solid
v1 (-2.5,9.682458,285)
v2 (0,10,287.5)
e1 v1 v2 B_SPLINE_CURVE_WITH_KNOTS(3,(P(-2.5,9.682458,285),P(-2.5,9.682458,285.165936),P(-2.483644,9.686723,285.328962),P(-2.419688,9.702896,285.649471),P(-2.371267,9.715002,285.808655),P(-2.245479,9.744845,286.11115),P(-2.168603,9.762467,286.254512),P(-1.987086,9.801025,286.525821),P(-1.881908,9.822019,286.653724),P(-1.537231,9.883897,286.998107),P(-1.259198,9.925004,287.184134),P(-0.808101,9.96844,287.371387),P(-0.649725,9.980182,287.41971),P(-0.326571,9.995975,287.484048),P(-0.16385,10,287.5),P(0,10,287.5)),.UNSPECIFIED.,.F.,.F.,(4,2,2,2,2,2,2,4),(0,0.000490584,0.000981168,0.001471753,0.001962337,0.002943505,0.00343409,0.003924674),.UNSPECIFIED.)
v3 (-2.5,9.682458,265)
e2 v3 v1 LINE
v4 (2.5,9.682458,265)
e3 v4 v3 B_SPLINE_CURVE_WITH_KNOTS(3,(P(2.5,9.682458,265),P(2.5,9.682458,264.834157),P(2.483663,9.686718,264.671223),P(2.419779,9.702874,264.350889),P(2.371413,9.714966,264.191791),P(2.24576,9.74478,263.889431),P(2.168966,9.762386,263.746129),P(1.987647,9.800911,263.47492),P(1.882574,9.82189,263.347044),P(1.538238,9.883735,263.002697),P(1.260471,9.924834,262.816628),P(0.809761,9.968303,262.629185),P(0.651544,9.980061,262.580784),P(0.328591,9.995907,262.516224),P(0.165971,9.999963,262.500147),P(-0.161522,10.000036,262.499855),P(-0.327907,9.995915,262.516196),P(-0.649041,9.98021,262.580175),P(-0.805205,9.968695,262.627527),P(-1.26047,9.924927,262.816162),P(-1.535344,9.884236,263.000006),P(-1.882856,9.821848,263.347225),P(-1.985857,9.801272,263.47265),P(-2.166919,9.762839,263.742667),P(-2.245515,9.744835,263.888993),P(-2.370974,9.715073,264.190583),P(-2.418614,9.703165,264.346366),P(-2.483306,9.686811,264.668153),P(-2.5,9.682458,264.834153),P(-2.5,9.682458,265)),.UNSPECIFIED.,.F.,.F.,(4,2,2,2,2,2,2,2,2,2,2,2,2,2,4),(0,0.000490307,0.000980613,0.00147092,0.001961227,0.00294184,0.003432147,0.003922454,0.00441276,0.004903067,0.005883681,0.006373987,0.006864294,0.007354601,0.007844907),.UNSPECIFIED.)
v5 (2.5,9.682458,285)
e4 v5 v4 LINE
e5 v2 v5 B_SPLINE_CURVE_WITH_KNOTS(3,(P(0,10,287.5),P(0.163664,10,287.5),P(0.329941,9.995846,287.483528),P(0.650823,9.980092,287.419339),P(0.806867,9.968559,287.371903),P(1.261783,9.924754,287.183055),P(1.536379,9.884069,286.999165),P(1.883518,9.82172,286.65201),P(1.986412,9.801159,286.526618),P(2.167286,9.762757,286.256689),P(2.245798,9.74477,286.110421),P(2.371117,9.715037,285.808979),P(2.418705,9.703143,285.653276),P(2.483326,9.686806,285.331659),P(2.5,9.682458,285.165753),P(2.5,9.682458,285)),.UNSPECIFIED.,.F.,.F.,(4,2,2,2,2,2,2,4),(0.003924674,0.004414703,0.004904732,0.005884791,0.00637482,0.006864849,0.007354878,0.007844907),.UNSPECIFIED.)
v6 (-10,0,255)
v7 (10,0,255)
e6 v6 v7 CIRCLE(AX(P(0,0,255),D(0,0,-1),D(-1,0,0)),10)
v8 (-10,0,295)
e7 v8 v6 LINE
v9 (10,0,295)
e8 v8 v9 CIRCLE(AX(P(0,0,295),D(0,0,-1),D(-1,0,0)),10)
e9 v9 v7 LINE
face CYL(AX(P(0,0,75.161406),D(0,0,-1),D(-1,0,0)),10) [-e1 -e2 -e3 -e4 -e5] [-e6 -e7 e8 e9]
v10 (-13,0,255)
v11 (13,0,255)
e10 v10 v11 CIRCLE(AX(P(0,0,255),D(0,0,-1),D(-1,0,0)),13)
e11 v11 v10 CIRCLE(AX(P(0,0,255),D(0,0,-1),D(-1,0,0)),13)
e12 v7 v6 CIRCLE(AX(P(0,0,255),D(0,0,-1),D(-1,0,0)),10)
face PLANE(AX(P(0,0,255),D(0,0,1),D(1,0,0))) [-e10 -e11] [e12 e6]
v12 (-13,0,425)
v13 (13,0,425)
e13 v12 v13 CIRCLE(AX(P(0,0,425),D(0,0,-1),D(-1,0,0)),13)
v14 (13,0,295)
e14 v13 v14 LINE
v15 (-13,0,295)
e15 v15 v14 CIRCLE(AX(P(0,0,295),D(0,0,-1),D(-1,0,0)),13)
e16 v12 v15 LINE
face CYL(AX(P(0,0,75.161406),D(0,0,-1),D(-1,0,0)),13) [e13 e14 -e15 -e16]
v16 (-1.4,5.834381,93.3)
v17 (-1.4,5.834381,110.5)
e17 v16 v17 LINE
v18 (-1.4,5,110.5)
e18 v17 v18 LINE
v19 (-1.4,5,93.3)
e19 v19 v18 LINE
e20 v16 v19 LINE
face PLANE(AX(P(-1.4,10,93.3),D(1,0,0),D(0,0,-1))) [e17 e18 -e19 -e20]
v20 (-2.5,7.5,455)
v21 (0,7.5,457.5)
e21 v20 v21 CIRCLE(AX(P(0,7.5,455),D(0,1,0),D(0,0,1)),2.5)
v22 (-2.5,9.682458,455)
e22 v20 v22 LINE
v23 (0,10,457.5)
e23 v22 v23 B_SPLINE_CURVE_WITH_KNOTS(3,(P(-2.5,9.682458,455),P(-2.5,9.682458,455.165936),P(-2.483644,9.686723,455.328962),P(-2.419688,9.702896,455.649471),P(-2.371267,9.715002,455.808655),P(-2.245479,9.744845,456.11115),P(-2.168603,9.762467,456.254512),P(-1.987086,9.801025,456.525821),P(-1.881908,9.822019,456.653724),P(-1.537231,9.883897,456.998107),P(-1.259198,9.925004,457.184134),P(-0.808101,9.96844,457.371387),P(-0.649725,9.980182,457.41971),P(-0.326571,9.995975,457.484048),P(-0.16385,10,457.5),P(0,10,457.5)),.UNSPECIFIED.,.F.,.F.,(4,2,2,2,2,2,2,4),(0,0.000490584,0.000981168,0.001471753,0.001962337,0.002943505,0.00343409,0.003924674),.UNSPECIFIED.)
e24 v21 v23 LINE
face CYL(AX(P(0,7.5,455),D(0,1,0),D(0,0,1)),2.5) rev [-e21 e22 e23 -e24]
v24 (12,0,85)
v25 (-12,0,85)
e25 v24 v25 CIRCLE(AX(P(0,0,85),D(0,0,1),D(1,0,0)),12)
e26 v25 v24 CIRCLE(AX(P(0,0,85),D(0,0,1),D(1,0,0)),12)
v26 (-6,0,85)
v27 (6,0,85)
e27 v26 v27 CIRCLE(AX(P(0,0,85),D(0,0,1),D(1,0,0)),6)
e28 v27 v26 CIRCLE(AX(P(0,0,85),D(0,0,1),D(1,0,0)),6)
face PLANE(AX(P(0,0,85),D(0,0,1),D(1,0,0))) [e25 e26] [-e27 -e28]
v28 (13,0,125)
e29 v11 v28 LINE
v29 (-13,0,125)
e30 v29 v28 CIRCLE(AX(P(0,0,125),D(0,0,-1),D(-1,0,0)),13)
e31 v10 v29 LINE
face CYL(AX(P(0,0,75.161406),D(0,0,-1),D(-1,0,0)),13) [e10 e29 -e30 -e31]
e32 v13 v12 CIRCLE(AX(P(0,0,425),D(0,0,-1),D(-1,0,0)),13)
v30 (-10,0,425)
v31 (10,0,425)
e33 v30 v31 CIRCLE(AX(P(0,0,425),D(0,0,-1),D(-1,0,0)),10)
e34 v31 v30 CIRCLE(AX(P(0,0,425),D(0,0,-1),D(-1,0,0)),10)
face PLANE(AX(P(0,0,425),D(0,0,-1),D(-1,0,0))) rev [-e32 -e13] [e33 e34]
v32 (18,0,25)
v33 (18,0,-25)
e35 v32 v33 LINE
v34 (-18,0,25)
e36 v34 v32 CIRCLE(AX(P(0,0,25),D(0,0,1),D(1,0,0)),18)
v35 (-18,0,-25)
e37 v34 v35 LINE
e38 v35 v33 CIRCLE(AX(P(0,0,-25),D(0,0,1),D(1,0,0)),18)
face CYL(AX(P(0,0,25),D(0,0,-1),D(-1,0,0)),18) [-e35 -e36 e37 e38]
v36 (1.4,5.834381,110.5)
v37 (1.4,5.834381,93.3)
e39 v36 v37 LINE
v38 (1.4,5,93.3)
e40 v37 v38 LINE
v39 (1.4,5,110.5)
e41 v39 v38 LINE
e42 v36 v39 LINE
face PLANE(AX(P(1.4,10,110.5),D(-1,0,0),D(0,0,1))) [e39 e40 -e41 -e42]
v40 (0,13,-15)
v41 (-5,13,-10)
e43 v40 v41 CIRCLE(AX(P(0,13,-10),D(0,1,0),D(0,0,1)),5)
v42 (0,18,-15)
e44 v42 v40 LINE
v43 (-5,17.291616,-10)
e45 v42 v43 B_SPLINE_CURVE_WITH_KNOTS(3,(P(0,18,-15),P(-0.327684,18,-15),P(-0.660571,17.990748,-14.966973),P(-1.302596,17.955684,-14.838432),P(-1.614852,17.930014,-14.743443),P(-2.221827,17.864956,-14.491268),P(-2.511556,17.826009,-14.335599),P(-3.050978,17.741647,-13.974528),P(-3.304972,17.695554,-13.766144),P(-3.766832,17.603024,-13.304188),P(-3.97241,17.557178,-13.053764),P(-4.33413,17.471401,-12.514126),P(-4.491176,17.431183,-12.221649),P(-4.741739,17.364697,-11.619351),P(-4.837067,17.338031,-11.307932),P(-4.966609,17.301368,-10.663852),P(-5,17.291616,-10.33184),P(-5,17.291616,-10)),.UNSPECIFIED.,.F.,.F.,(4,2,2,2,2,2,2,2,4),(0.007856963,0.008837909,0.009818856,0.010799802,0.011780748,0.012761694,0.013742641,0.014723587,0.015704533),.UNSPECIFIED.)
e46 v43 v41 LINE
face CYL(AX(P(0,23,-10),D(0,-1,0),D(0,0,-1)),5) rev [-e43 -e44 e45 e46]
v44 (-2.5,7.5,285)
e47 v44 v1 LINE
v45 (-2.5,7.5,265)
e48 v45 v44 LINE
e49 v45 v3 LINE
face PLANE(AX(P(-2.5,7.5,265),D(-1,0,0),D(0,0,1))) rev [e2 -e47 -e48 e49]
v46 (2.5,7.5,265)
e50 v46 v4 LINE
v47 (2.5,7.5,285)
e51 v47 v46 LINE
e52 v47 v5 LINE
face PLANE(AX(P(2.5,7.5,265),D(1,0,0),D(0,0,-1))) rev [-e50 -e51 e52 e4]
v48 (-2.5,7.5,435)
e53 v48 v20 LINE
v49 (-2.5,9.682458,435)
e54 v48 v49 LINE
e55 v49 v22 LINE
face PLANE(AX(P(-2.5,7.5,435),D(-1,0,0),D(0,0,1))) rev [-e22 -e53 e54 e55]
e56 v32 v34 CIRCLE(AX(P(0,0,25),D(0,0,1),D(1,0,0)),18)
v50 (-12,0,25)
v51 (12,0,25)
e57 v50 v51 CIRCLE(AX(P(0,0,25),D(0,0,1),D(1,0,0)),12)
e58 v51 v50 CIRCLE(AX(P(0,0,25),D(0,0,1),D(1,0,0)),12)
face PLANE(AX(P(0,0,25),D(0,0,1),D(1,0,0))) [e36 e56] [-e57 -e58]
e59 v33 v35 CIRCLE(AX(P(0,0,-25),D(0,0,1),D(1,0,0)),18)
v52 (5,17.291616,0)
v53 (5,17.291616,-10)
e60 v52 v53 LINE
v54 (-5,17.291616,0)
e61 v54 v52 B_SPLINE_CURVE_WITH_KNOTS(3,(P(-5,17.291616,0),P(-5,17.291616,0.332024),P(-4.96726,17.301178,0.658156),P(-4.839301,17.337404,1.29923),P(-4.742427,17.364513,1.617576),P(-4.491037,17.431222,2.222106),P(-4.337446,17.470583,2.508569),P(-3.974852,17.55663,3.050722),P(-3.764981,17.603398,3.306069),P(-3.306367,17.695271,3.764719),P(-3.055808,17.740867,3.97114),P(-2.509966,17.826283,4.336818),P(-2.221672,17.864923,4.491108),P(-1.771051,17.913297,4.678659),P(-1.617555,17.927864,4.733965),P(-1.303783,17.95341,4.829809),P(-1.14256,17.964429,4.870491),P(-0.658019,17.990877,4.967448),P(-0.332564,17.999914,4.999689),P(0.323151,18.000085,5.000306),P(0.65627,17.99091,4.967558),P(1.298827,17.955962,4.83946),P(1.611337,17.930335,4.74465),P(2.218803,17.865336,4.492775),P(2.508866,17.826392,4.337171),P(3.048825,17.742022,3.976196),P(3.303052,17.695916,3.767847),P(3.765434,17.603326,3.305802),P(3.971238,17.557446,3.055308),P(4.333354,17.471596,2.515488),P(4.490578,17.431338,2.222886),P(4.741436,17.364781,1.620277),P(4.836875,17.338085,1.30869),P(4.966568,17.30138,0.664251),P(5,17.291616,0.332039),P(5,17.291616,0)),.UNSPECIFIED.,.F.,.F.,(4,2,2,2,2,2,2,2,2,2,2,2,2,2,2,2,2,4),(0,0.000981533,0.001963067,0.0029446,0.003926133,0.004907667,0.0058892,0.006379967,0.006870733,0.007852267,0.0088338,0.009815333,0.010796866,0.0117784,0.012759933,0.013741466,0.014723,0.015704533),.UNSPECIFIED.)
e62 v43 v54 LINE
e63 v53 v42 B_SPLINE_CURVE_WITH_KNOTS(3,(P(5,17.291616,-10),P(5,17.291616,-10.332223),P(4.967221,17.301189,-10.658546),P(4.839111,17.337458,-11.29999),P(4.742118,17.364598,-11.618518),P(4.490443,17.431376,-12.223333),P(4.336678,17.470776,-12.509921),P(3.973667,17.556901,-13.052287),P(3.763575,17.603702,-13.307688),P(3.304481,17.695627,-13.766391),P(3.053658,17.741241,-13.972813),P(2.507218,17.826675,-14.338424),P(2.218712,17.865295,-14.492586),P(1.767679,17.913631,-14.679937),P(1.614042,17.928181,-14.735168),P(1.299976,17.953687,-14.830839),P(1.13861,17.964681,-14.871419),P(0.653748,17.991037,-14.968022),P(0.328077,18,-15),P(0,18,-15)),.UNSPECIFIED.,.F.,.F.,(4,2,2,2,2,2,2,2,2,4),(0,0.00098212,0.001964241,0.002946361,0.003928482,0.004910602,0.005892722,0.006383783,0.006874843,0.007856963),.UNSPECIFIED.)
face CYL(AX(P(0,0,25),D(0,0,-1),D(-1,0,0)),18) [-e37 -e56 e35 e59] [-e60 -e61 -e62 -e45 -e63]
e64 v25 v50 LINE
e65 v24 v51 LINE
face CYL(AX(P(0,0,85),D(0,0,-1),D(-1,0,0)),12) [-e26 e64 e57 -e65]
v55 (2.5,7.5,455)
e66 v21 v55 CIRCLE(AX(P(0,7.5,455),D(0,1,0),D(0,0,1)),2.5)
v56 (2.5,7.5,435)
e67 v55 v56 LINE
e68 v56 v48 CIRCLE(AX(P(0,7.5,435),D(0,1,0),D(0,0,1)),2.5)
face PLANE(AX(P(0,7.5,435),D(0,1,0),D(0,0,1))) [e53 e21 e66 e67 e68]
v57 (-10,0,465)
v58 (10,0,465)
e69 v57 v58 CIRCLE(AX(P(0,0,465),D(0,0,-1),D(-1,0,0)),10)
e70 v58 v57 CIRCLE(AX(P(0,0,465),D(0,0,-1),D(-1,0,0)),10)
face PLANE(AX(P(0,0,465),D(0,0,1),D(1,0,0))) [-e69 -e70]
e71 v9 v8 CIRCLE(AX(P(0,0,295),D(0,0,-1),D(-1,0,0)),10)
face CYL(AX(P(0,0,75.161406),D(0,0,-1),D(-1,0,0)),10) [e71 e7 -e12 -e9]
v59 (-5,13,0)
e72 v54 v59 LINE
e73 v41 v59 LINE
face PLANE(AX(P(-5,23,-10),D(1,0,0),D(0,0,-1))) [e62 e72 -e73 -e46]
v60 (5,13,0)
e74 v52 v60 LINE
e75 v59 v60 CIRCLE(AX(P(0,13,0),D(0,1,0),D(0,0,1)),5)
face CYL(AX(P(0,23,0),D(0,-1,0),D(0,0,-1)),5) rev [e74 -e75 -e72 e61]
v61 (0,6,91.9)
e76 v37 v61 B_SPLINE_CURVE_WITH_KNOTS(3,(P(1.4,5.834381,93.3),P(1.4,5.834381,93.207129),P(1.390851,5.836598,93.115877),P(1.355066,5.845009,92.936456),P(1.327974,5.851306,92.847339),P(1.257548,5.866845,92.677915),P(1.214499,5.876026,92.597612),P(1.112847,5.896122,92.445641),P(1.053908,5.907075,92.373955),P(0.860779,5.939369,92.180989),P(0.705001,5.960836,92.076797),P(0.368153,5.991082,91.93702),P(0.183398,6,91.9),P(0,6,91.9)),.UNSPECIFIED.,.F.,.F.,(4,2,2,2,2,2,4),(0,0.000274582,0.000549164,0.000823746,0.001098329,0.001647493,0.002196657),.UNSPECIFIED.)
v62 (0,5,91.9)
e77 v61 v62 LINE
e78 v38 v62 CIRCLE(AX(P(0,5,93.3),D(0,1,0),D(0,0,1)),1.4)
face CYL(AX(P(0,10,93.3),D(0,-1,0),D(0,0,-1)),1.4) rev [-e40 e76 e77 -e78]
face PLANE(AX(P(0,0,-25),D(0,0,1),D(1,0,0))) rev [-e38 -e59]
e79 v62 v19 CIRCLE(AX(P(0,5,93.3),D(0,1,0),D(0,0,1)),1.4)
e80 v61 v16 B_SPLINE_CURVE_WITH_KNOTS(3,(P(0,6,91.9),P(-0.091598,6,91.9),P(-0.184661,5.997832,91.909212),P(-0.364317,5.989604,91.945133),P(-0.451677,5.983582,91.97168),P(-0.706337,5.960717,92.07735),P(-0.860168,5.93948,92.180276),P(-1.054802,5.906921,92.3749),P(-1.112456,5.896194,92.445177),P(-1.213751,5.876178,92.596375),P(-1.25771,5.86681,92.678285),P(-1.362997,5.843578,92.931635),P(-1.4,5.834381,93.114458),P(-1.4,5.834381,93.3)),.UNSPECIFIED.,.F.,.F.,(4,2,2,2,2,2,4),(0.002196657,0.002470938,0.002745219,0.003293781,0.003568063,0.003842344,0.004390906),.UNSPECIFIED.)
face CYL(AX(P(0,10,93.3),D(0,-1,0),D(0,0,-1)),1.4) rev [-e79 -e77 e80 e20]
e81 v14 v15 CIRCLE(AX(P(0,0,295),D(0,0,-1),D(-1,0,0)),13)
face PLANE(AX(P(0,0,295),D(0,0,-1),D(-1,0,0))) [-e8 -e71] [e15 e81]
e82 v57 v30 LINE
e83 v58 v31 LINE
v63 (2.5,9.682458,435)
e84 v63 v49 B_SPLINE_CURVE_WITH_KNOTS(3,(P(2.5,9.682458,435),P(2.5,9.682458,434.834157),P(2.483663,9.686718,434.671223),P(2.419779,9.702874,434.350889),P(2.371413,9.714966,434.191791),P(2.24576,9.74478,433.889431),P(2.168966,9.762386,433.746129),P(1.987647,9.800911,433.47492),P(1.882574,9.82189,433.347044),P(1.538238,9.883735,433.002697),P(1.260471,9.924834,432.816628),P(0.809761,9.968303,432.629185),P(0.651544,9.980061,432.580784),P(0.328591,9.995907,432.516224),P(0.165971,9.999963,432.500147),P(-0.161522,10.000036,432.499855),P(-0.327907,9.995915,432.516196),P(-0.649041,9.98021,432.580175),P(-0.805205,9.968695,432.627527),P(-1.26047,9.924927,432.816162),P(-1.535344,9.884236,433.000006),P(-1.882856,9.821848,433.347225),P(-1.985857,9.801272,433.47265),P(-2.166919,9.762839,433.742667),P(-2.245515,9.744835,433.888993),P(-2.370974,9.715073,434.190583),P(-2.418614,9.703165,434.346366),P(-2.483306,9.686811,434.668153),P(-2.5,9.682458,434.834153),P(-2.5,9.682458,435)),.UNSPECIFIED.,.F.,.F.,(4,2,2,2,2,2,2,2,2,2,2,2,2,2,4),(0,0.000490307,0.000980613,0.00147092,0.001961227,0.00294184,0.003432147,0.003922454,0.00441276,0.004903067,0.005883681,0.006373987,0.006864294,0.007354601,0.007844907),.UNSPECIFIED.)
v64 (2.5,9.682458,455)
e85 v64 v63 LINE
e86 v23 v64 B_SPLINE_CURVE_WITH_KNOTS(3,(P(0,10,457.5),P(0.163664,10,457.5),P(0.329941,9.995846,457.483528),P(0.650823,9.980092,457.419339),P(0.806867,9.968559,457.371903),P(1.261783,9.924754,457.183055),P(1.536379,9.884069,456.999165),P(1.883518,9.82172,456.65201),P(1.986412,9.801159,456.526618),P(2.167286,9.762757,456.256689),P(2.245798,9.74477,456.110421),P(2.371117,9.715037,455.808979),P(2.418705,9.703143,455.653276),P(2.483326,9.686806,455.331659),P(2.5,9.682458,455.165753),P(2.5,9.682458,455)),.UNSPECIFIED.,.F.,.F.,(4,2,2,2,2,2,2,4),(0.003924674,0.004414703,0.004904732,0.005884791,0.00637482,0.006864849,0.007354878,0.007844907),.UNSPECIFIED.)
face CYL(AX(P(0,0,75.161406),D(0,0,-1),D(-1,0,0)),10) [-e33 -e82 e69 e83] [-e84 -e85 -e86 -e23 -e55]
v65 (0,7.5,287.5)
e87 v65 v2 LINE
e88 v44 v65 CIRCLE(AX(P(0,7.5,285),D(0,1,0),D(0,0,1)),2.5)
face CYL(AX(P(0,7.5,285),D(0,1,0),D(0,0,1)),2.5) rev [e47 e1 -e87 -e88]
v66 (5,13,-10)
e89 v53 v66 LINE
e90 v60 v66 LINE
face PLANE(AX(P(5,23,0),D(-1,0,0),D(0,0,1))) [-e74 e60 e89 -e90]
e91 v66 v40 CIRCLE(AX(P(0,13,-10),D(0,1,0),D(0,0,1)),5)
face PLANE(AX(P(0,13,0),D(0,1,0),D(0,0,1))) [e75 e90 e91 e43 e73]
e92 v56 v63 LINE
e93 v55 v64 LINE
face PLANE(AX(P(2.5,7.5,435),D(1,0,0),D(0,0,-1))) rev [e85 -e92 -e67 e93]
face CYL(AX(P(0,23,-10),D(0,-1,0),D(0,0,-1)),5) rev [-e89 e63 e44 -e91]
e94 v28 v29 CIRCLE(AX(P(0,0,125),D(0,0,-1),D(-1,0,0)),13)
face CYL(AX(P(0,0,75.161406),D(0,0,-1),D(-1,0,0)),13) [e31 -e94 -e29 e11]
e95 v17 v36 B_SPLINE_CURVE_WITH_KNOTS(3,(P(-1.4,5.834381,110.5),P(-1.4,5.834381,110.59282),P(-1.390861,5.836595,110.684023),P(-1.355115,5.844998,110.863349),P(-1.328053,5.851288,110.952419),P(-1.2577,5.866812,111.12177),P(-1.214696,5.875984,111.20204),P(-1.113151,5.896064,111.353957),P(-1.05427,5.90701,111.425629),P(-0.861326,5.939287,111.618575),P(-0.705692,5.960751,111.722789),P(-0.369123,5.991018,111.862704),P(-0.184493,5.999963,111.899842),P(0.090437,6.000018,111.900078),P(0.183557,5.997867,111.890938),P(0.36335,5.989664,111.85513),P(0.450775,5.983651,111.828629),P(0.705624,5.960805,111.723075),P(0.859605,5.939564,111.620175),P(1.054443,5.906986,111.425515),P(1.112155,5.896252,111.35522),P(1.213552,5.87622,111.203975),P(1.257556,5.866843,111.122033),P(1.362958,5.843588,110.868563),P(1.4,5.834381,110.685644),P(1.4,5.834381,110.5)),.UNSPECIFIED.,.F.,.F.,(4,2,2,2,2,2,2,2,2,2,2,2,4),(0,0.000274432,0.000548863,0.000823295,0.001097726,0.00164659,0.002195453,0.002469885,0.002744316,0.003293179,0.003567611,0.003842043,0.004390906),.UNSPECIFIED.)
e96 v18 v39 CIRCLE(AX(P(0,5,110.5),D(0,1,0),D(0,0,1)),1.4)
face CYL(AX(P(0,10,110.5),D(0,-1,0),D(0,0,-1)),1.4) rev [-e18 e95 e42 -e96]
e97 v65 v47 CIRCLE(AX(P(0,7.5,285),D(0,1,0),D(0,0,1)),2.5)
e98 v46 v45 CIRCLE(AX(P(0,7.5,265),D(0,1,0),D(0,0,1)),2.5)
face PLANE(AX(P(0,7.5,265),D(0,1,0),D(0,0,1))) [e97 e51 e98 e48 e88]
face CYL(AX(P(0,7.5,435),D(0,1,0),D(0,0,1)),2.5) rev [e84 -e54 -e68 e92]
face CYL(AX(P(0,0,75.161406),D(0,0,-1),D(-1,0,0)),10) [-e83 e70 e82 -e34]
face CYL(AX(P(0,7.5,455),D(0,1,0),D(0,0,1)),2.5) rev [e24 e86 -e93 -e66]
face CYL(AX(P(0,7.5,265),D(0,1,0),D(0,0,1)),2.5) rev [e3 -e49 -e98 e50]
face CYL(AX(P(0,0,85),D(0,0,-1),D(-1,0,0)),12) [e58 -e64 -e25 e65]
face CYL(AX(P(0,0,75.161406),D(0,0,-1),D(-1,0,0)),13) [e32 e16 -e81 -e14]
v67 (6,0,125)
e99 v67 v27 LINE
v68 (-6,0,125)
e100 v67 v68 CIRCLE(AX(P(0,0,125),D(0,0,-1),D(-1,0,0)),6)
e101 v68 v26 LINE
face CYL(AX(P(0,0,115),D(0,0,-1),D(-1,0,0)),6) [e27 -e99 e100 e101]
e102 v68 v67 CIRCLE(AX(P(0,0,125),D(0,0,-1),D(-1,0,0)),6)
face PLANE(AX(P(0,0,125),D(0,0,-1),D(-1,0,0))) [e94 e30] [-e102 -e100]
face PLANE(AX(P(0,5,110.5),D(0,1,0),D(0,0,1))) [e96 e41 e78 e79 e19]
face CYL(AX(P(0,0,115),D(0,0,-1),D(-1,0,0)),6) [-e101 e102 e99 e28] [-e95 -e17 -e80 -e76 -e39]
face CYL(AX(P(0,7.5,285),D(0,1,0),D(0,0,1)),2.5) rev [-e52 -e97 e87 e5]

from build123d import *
from build123d.topology import SkipClean

# Parameters (mm, degrees)
SKETCH1_R           = 18
BOSS_EXTRUDE2_DEPTH = 25
SKETCH6_R           = 12
BOSS_EXTRUDE6_DEPTH = 60
SKETCH7_R           = 6
BOSS_EXTRUDE7_DEPTH = 30
CUT_EXTRUDE3_DEPTH  = 10
CUT_EXTRUDE4_DEPTH  = 5
CUT_EXTRUDE5_DEPTH  = 2.5
CUT_EXTRUDE6_DEPTH  = 2.5


with BuildPart() as part:
    # Sketch1 → Boss-Extrude2 (new, symmetric)
    with BuildSketch(Plane.XY):
        Circle(SKETCH1_R)
    extrude(amount=BOSS_EXTRUDE2_DEPTH, both=True)

    # Sketch6 → Boss-Extrude6 (add)
    with BuildSketch(Plane.XY.offset(25)):
        Circle(SKETCH6_R)
    extrude(amount=BOSS_EXTRUDE6_DEPTH)

    # Sketch7 → Boss-Extrude7 (add)
    with BuildSketch(Plane.XY.offset(85)):
        Circle(SKETCH7_R)
    extrude(amount=BOSS_EXTRUDE7_DEPTH)

    # Sketch11 → Cut-Extrude3 (cut)
    with BuildSketch(Plane(origin=(0, 13, 0), x_dir=(-1, 0, 0), z_dir=(0, 1, 0))):
        with BuildLine():
            Line((-5, 0), (-5, -10))
            ThreePointArc((-5, -10), (0, -15), (5, -10))
            Line((5, -10), (5, 0))
            ThreePointArc((5, 0), (0, 5), (-5, 0))
        make_face()
    extrude(amount=CUT_EXTRUDE3_DEPTH, mode=Mode.SUBTRACT)

    # Sketch12 → Cut-Extrude4 (cut)
    with BuildSketch(Plane(origin=(0, 5, 0), x_dir=(-1, 0, 0), z_dir=(0, 1, 0))):
        with BuildLine():
            Line((-1.4, 110.5), (-1.4, 93.3))
            ThreePointArc((-1.4, 93.3), (0, 91.9), (1.4, 93.3))
            Line((1.4, 93.3), (1.4, 110.5))
            ThreePointArc((1.4, 110.5), (0, 111.9), (-1.4, 110.5))
        make_face()
    extrude(amount=CUT_EXTRUDE4_DEPTH, mode=Mode.SUBTRACT)

    # Sketch13 → Revolve1 (revolve)
    with SkipClean():  # the faces are left unmerged after this step: merging them gives an invalid solid
        with BuildSketch(Plane(origin=(0, 0, 0), x_dir=(1, 0, 0), z_dir=(0, 1, 0))):
            Polygon((0, -465), (0, -115), (-6, -115), (-6, -125), (-13, -125), (-13, -255), (-10, -255), (-10, -295), (-13, -295), (-13, -425), (-10, -425), (-10, -465), align=None)
        revolve(axis=Axis((0, 0, 75.161405529), (0, 0, 1)))

    # Sketch16 → Cut-Extrude5 (cut)
    with SkipClean():  # the faces are left unmerged after this step: merging them gives an invalid solid
        with BuildSketch(Plane(origin=(0, 10, 0), x_dir=(1, 0, 0), z_dir=(0, 1, 0))):
            with BuildLine():
                Line((2.5, -265), (2.5, -285))
                ThreePointArc((2.5, -285), (0, -287.5), (-2.5, -285))
                Line((-2.5, -285), (-2.5, -265))
                ThreePointArc((-2.5, -265), (0, -262.5), (2.5, -265))
            make_face()
        extrude(amount=-CUT_EXTRUDE5_DEPTH, mode=Mode.SUBTRACT)

    # Sketch17 → Cut-Extrude6 (cut)
    with SkipClean():  # the faces are left unmerged after this step: merging them gives an invalid solid
        with BuildSketch(Plane(origin=(0, 10, 0), x_dir=(1, 0, 0), z_dir=(0, 1, 0))):
            with BuildLine():
                Line((2.5, -435), (2.5, -455))
                ThreePointArc((2.5, -455), (0, -457.5), (-2.5, -455))
                Line((-2.5, -455), (-2.5, -435))
                ThreePointArc((-2.5, -435), (0, -432.5), (2.5, -435))
            make_face()
        extrude(amount=-CUT_EXTRUDE6_DEPTH, mode=Mode.SUBTRACT)


solid = part.part
